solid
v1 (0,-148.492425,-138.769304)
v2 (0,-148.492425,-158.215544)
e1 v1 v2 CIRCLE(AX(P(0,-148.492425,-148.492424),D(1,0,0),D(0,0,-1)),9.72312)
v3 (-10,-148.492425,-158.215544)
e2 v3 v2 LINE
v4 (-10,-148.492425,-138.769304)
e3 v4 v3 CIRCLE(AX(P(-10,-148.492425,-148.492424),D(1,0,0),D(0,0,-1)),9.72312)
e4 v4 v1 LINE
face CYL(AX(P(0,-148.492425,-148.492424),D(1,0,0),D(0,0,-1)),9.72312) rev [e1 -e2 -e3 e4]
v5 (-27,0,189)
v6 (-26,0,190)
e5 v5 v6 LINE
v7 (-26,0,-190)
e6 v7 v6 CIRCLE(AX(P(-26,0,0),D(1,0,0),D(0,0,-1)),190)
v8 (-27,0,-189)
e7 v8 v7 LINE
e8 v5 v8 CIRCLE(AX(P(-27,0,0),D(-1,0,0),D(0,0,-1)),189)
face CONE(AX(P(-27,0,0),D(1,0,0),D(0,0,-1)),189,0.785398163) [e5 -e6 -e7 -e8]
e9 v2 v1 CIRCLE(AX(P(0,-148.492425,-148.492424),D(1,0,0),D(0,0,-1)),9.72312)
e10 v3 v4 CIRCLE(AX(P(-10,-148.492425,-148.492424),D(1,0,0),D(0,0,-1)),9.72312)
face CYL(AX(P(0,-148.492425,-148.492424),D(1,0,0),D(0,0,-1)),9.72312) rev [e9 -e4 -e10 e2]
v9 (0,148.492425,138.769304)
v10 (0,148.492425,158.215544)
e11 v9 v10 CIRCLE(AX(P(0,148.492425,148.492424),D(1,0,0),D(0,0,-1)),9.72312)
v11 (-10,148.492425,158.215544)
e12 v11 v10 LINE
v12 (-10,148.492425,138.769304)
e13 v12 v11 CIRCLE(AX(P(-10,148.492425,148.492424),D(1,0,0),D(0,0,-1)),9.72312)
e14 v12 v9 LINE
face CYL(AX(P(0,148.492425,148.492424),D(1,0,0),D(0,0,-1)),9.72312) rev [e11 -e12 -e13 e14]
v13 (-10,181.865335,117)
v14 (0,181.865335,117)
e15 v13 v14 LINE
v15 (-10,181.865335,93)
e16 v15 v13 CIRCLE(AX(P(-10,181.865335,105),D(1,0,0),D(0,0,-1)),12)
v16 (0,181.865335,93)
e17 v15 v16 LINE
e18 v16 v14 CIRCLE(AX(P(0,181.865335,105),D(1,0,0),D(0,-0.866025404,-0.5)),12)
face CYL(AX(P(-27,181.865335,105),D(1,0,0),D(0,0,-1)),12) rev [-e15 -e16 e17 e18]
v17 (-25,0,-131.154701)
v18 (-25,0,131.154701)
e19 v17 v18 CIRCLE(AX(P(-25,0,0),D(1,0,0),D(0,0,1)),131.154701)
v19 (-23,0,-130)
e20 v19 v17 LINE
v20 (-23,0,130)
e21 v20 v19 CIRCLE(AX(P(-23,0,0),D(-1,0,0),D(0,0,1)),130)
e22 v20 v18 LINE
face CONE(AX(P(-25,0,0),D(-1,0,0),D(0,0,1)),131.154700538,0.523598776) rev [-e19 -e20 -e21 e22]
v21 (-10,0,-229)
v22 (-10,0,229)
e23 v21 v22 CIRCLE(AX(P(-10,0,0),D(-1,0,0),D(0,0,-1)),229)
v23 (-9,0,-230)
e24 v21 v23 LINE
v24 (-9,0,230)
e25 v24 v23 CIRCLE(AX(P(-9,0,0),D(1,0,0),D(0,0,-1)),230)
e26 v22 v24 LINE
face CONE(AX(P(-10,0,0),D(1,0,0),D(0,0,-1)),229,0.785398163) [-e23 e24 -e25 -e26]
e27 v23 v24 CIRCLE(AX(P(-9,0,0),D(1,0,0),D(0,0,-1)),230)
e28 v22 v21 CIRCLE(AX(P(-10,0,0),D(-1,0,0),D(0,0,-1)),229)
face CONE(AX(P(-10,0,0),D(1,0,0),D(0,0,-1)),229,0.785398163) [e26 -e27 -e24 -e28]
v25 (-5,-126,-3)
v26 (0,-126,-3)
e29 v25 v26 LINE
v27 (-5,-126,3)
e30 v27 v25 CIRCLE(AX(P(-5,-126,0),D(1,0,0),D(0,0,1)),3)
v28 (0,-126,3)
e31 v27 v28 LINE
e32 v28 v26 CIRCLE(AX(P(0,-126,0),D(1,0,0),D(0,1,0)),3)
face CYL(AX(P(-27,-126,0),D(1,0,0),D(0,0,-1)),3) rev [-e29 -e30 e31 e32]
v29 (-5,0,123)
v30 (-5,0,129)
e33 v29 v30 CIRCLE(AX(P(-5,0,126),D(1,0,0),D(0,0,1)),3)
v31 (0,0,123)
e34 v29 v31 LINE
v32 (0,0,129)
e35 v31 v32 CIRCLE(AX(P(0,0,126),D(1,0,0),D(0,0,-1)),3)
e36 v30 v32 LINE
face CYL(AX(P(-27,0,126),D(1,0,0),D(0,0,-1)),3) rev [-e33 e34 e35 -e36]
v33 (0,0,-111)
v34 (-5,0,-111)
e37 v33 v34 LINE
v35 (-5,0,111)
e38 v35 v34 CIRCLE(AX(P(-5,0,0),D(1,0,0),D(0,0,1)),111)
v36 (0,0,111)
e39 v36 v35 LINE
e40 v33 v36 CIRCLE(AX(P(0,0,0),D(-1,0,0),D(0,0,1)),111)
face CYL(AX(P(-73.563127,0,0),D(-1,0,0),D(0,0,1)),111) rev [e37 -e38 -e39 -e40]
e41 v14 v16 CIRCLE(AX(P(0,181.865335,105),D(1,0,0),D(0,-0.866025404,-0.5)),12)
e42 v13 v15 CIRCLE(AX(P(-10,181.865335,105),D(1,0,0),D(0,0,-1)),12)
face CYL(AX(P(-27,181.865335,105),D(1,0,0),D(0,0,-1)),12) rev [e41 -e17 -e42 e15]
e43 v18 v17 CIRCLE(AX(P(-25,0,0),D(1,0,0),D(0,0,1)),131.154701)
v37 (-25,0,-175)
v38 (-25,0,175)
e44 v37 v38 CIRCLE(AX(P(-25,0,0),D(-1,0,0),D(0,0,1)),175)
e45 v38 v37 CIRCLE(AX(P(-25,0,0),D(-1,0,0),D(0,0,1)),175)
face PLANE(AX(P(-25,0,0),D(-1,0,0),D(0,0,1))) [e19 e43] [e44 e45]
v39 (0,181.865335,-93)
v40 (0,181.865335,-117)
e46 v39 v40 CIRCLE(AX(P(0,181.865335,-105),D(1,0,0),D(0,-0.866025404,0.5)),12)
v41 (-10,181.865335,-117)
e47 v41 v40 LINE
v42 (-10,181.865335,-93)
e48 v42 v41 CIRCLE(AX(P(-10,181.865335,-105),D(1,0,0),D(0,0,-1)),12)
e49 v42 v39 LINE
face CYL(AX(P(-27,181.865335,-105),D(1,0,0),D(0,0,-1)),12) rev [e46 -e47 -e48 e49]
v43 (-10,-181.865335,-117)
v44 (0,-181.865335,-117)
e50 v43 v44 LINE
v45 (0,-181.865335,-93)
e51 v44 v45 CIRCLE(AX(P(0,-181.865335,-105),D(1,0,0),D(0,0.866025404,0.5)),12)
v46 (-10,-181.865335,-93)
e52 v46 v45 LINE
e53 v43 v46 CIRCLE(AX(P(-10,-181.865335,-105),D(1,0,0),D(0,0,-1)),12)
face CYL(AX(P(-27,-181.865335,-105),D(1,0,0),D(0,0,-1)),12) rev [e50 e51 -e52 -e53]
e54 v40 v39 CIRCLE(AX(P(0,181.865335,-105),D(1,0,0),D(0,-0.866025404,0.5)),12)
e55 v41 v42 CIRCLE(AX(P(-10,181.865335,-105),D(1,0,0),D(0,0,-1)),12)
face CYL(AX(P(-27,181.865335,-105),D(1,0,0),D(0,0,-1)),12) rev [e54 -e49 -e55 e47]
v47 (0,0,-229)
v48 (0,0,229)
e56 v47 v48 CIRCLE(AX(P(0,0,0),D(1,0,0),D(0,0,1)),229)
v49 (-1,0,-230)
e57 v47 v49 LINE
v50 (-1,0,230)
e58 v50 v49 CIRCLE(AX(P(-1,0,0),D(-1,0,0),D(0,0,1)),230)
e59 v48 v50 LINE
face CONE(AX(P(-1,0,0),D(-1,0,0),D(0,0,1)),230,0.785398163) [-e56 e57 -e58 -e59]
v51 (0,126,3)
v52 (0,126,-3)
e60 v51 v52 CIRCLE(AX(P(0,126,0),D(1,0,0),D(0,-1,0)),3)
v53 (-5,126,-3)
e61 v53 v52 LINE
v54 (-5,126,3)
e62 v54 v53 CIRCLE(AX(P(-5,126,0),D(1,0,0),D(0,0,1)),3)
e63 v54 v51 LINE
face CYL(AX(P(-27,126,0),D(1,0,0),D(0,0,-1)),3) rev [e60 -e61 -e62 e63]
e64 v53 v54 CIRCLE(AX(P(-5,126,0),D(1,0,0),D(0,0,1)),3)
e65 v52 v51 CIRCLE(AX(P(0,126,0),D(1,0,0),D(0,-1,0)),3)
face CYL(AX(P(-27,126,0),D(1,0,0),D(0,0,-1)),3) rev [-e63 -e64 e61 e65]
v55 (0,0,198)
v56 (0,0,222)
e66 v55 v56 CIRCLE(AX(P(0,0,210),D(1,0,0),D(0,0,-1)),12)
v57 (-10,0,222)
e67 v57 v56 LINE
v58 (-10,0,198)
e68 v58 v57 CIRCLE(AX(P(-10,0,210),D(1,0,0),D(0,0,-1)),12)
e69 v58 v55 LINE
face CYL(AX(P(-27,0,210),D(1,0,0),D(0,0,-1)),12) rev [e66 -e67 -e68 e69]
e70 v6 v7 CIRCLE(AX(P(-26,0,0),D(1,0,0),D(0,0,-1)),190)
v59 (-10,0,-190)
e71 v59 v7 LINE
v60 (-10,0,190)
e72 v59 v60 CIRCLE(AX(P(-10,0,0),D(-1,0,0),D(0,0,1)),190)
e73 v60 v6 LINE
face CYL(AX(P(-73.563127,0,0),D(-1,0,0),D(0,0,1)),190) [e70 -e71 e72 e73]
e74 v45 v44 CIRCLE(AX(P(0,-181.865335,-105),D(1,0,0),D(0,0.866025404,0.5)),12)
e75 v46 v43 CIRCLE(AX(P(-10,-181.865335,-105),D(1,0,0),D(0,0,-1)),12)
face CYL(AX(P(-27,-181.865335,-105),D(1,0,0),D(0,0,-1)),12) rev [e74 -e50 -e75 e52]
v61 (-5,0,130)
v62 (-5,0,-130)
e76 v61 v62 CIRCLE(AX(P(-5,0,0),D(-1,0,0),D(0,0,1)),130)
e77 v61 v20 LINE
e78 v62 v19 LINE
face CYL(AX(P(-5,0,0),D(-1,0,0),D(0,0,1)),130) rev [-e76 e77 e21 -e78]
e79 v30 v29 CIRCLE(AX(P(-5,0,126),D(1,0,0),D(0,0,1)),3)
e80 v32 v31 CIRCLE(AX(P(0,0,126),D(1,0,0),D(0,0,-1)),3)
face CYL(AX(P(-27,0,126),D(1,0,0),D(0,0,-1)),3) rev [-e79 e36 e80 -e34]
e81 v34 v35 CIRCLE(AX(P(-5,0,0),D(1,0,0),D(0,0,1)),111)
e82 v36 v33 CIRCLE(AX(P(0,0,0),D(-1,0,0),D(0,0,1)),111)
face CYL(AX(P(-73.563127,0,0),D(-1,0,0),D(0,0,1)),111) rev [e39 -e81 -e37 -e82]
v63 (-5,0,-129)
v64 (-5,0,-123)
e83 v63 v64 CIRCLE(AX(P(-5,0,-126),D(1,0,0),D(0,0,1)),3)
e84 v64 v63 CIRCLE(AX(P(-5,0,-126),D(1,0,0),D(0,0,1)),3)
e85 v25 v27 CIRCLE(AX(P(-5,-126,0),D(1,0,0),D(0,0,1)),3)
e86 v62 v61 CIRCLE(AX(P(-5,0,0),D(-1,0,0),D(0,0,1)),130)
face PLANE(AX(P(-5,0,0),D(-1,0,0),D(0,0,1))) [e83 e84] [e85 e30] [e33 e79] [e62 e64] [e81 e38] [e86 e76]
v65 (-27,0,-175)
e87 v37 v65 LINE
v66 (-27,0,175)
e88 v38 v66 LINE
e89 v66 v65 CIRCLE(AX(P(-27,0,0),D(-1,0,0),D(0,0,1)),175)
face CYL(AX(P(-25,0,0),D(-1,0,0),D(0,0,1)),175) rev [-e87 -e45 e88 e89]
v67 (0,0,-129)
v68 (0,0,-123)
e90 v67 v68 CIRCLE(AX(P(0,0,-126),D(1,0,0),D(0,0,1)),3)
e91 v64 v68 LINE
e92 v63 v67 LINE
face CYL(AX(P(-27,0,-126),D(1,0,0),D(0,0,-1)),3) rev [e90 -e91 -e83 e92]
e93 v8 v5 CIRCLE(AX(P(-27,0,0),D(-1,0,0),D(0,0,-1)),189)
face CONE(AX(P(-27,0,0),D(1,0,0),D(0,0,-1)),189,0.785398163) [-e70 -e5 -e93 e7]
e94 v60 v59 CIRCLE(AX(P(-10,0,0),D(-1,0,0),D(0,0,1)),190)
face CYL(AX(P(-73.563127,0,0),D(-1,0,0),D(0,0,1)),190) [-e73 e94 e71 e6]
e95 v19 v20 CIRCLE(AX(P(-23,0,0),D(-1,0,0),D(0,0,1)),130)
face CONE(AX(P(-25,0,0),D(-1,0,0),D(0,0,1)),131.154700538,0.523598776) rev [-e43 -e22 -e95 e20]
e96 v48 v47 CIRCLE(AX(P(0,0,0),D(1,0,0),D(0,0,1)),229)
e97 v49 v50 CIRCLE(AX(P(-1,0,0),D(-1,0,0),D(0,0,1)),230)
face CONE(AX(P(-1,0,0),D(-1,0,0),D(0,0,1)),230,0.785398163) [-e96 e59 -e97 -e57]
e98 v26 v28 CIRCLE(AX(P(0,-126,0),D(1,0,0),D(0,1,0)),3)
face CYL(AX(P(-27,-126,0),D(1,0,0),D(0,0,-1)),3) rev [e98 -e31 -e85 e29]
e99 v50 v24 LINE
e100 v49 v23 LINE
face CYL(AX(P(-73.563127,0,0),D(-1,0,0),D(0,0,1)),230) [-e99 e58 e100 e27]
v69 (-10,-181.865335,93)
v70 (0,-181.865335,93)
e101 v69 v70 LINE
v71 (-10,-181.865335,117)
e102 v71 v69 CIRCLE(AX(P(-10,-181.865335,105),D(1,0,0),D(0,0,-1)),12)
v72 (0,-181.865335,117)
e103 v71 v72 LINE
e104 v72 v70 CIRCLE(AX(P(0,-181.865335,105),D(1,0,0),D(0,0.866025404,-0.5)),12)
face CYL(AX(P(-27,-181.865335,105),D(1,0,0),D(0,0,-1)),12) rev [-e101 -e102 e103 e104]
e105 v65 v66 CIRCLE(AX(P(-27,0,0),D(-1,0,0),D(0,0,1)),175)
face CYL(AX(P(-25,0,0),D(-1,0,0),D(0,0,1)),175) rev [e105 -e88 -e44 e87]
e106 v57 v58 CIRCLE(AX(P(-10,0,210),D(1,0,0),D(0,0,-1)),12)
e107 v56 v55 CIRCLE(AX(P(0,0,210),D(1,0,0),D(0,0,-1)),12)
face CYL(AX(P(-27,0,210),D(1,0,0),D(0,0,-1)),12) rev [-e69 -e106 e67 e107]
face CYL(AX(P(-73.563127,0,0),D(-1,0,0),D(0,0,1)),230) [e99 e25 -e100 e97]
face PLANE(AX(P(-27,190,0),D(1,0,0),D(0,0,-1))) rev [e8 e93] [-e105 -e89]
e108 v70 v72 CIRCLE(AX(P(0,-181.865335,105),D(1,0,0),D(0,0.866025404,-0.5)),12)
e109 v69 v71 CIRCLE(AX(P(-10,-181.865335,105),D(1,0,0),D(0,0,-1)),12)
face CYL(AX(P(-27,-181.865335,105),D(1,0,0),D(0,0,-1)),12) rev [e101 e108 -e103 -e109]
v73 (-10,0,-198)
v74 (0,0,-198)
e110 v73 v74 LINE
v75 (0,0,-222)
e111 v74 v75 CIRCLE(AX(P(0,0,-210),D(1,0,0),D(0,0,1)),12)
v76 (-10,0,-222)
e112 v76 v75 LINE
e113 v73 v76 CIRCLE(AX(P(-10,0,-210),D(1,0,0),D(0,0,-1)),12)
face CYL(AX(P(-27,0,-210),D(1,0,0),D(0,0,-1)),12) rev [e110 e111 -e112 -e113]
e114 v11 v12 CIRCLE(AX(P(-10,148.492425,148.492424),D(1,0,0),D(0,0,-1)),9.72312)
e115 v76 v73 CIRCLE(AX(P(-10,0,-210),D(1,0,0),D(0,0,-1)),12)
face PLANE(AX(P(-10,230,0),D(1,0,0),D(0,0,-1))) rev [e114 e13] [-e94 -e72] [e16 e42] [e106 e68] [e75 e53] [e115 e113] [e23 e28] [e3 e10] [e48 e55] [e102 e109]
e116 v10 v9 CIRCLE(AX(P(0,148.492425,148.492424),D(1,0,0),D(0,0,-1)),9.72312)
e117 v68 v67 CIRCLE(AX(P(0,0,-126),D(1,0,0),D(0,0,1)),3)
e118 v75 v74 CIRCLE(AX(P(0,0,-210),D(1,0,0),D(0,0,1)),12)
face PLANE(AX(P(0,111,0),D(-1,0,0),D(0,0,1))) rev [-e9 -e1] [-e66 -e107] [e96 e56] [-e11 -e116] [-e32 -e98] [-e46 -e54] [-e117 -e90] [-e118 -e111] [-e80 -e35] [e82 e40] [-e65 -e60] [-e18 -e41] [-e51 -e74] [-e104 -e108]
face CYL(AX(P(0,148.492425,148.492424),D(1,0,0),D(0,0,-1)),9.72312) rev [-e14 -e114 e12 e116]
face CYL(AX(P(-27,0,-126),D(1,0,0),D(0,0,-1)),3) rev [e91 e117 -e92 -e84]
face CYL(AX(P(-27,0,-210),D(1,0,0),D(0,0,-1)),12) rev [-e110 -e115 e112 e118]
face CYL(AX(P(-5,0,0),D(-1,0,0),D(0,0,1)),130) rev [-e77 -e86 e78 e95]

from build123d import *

# Parameters (mm, degrees)
SKETCH3_R              = 12
CUT_EXTRUDE1_DEPTH     = 327.387806145
CIRPATTERN1_COUNT      = 6
SKETCH4_R              = 3
CUT_EXTRUDE5_DEPTH     = 327.387806145
CIRPATTERN2_COUNT      = 4
SKETCH5_R              = 130
CUT_EXTRUDE6_DEPTH     = 22
SKETCH6_R              = 175
CUT_EXTRUDE7_DEPTH     = 2
CHAMFER2_SIZE          = 2
CHAMFER2_SIZE2         = 1.154700538
CHAMFER3_SIZE          = 1
F_7_8_9_TAPPED_HOLE1_D = 19.44624
CIRPATTERN4_COUNT      = 2


with BuildPart() as part:
    # Sketch1 → Revolve1 (revolve)
    with BuildSketch(Plane.XY, mode=Mode.PRIVATE) as revolve1_sk:
        Polygon((0, 111), (0, 230), (-10, 230), (-10, 190), (-27, 190), (-27, 111), align=None)
    revolve(revolve1_sk.sketch.rotate(Axis((-73.563127278, 0, 0), (1, 0, 0)), 90), axis=Axis((-73.563127278, 0, 0), (1, 0, 0)))

    # Sketch3 → Cut-Extrude1 (cut, through all)
    with BuildSketch(Plane(origin=(0, 0, 0), x_dir=(0, 0, -1), z_dir=(1, 0, 0))):
        with Locations((-210, 0)):
            Circle(SKETCH3_R)
    cut_extrude1 = extrude(amount=-CUT_EXTRUDE1_DEPTH, mode=Mode.SUBTRACT)

    # CirPattern1: Cut-Extrude1 ×6 about axis
    cirpattern1_axis = Axis((0, 0, 0), (1, 0, 0))
    for i in range(1, CIRPATTERN1_COUNT):
        add(cut_extrude1.rotate(cirpattern1_axis, i * 360 / CIRPATTERN1_COUNT), mode=Mode.SUBTRACT)

    # Sketch4 → Cut-Extrude5 (cut, through all)
    with BuildSketch(Plane(origin=(0, 0, 0), x_dir=(0, 0, -1), z_dir=(1, 0, 0))):
        with Locations((-126, 0)):
            Circle(SKETCH4_R)
    cut_extrude5 = extrude(amount=-CUT_EXTRUDE5_DEPTH, mode=Mode.SUBTRACT)

    # CirPattern2: Cut-Extrude5 ×4 about axis
    cirpattern2_axis = Axis((0, 0, 0), (1, 0, 0))
    for i in range(1, CIRPATTERN2_COUNT):
        add(cut_extrude5.rotate(cirpattern2_axis, i * 360 / CIRPATTERN2_COUNT), mode=Mode.SUBTRACT)

    # Sketch5 → Cut-Extrude6 (cut)
    with BuildSketch(Plane.ZY.offset(27)):
        Circle(SKETCH5_R)
    extrude(amount=-CUT_EXTRUDE6_DEPTH, mode=Mode.SUBTRACT)

    # Sketch6 → Cut-Extrude7 (cut)
    with BuildSketch(Plane.ZY.offset(27)):
        Circle(SKETCH6_R)
    extrude(amount=-CUT_EXTRUDE7_DEPTH, mode=Mode.SUBTRACT)

    # Chamfer2
    chamfer2_edges = [part.edges().sort_by_distance(p)[0] for p in [
        (-25, 0, -130),
    ]]
    chamfer2_side = [part.faces().sort_by_distance(p)[0] for p in [
        (-15, 0, -130),
    ]]
    chamfer(chamfer2_edges, length=CHAMFER2_SIZE, length2=CHAMFER2_SIZE2, reference=chamfer2_side[0])

    # Chamfer3
    chamfer3_edges = [part.edges().sort_by_distance(p)[0] for p in [
        (0, 0, -230),
        (-27, 0, -190),
        (-10, 0, -230),
    ]]
    chamfer(chamfer3_edges, length=CHAMFER3_SIZE)

    # 7/8-9 Tapped Hole1 (through all)
    with Locations(Plane(origin=(0, 148.492424572, 148.492423527), x_dir=(0, 0, 1), z_dir=(1, 0, 0))):
        with Locations((0, 0)):
            f_7_8_9_tapped_hole1 = Hole(F_7_8_9_TAPPED_HOLE1_D / 2)

    # CirPattern4: 7/8-9 Tapped Hole1 ×2 about axis
    cirpattern4_axis = Axis((0, 0, 0), (1, 0, 0))
    for i in range(1, CIRPATTERN4_COUNT):
        add(f_7_8_9_tapped_hole1.rotate(cirpattern4_axis, i * 360 / CIRPATTERN4_COUNT), mode=Mode.SUBTRACT)


solid = part.part
